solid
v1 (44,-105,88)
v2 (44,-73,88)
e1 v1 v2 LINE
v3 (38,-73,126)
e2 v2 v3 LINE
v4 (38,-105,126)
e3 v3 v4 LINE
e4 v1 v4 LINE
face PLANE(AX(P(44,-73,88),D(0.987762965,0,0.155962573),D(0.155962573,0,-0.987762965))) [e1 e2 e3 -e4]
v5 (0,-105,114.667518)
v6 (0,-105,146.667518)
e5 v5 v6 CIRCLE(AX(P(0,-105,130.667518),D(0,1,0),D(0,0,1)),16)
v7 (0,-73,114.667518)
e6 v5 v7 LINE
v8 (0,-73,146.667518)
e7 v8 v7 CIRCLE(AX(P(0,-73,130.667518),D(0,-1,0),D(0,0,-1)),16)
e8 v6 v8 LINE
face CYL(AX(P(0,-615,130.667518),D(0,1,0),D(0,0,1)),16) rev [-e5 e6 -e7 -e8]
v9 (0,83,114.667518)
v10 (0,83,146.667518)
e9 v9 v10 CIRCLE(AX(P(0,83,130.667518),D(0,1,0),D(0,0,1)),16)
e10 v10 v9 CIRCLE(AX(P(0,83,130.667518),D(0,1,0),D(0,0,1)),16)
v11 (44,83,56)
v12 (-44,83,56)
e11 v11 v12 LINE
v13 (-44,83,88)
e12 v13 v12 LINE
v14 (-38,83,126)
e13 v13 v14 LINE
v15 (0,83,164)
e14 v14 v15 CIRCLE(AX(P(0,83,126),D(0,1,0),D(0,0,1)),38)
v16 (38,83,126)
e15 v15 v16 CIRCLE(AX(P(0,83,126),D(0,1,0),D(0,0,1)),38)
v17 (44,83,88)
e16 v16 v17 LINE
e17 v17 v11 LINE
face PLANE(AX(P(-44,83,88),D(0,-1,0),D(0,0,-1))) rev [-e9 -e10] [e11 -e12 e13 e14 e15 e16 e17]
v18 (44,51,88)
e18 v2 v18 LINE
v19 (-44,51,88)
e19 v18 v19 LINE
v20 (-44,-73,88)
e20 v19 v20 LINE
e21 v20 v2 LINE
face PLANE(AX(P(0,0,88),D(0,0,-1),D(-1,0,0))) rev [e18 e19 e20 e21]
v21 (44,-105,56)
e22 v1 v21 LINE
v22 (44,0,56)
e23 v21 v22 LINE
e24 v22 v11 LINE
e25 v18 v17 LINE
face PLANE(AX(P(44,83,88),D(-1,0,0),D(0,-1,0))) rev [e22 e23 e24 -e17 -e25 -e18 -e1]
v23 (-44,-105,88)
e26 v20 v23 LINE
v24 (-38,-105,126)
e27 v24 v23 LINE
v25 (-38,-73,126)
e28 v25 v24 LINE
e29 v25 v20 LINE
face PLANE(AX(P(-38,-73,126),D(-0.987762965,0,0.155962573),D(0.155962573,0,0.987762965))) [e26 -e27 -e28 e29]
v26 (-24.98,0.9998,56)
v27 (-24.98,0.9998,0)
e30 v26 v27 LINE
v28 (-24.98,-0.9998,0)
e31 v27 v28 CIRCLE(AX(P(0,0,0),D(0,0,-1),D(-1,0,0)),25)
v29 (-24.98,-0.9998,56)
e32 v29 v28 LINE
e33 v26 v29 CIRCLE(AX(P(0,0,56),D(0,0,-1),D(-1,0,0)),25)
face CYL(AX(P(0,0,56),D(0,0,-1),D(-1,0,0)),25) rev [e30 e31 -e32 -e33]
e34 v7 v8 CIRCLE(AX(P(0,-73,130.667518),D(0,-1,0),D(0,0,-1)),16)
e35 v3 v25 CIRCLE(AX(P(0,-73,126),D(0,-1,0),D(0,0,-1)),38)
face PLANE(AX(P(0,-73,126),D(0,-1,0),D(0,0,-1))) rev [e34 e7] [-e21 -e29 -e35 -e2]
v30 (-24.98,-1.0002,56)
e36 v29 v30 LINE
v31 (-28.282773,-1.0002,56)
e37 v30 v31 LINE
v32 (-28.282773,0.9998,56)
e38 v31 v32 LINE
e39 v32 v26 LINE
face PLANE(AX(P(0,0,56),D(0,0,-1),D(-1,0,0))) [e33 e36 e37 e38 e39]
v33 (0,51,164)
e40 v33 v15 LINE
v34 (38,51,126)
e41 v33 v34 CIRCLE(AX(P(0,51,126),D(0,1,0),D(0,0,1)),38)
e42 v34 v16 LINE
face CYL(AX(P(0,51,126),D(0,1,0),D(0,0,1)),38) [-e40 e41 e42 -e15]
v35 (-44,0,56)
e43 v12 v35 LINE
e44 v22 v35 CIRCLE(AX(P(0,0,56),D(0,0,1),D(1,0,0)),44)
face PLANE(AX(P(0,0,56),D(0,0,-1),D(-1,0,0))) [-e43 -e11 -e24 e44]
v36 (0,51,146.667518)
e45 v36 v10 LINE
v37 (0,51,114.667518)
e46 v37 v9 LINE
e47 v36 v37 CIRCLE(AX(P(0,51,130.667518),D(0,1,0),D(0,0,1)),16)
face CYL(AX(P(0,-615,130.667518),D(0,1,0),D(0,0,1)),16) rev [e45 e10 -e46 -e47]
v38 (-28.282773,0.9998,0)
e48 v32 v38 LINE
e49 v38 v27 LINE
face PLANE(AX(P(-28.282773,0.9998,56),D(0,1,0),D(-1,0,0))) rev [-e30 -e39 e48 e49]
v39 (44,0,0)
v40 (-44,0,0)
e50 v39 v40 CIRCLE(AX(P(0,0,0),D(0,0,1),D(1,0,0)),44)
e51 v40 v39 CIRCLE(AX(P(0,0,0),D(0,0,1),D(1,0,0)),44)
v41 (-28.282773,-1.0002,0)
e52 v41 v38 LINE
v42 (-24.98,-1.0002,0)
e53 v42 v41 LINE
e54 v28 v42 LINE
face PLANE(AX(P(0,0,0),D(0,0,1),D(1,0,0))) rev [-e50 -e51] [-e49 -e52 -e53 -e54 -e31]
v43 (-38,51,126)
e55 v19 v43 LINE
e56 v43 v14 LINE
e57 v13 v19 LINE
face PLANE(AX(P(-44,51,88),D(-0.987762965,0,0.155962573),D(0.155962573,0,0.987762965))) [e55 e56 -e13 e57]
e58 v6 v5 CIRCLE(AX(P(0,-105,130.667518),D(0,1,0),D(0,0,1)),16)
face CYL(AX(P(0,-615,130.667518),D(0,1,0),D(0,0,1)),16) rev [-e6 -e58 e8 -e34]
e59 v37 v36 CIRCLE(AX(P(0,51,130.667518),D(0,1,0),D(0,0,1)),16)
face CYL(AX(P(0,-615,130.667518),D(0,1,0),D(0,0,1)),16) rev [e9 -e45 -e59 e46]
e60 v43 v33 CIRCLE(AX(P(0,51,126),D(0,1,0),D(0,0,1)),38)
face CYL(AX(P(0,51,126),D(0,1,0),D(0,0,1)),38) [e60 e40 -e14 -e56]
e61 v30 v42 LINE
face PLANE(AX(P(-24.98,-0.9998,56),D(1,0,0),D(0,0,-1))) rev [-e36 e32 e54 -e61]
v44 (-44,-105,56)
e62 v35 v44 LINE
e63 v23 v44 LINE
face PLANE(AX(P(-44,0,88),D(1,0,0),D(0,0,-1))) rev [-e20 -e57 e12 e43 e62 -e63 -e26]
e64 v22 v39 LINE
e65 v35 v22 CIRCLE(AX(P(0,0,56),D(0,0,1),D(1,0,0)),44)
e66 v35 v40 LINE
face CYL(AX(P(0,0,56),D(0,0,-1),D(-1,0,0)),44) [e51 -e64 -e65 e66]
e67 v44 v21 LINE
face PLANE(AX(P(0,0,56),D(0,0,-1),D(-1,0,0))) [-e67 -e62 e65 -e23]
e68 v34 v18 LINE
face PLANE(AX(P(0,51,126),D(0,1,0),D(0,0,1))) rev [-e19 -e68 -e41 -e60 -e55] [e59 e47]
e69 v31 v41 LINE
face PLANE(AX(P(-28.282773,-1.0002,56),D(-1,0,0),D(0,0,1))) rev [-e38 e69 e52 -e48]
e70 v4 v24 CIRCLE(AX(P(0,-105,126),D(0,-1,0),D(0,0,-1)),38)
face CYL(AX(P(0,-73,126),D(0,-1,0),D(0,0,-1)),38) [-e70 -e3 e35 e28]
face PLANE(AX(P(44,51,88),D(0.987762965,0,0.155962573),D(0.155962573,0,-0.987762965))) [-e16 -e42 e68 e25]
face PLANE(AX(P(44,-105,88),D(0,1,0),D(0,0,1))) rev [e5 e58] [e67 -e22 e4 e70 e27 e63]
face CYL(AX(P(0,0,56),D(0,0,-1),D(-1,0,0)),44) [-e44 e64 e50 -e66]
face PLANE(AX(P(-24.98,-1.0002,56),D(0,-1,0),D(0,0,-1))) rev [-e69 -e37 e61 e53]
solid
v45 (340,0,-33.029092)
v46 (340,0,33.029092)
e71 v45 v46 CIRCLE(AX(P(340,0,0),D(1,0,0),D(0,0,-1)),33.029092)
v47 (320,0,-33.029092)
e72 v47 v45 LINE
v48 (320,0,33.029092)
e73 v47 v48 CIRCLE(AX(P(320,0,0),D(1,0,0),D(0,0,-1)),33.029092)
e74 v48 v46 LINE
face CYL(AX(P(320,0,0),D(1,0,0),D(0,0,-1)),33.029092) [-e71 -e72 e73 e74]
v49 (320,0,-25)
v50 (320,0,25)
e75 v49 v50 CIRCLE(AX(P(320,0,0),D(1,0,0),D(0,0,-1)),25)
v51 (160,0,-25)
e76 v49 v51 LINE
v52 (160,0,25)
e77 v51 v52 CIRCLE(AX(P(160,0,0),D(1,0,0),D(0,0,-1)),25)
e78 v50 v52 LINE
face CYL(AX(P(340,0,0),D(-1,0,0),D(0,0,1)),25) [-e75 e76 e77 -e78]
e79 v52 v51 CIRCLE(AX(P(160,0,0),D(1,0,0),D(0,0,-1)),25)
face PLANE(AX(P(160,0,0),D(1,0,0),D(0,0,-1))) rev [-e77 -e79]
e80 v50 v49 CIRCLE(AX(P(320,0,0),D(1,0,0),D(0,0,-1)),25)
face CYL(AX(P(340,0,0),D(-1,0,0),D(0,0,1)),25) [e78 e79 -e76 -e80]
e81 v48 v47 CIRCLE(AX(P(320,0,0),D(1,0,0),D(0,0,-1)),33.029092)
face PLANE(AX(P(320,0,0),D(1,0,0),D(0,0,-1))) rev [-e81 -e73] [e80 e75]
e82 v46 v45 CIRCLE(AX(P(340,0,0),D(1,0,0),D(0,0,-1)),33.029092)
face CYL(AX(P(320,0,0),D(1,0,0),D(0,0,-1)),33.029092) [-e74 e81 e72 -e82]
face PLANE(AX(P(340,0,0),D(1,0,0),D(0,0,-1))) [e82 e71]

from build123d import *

# Parameters (mm, degrees)
HUB_PROFILE_88_R                  = 44
HUB_BOSS_88_DEPTH                 = 56
HUB_CUT_DEPTH                     = 56
YOKE_BASE_PLATE_DEPTH             = 32
YOKE_ARMS_DEPTH                   = 32
YOKE_START                        = -32
YOKE_WEB_DEPTH                    = 32
CROSS_PIN_BORE_PROFILE_R          = 16
CROSS_PIN_BORE_THROUGH_LUGS_DEPTH = 698
PIN_SHAFT_PROFILE_50_R            = 25
PIN_SHAFT_50_DEPTH                = 180
PIN_HEAD_PROFILE_R                = 33.029092334
PIN_HEAD_DEPTH                    = 20


with BuildPart() as part:
    # Hub Profile Ø88 → Hub Boss Ø88 (new body)
    with BuildSketch(Plane.XY):
        Circle(HUB_PROFILE_88_R)
    extrude(amount=HUB_BOSS_88_DEPTH)

    # Hub Cut Profile → Hub Cut (cut)
    with BuildSketch(Plane(origin=(0, 0, 0), x_dir=(-1, 0, 0), z_dir=(0, 0, -1))):
        with BuildLine():
            Line((24.98, -0.99979998), (28.282772946, -1.00020002))
            Line((28.282772946, -1.00020002), (28.282772946, 0.99979998))
            Line((28.282772946, 0.99979998), (24.98, 0.99979998))
            ThreePointArc((24.98, 0.99979998), (-25, 0), (24.98, -0.99979998))
        make_face()
    extrude(amount=-HUB_CUT_DEPTH, mode=Mode.SUBTRACT)

    # Yoke Base Profile → Yoke Base Plate (add)
    with BuildSketch(Plane.XY.offset(56)):
        Polygon((-44, 0), (-44, 83), (44, 83), (44, -105), (-44, -105), align=None)
    extrude(amount=YOKE_BASE_PLATE_DEPTH)

    # Yoke Arms Profile → Yoke Arms (add)
    with BuildSketch(Plane(origin=(0, 83, 0), x_dir=(1, 0, 0), z_dir=(0, 1, 0))):
        with BuildLine():
            Line((-44, -88), (44, -88))
            Line((44, -88), (38, -126))
            ThreePointArc((38, -126), (0, -164), (-38, -126))
            Line((-38, -126), (-44, -88))
        make_face()
    extrude(amount=-YOKE_ARMS_DEPTH)

    # Yoke Web Profile → Yoke Web (add)
    with BuildSketch(Plane.XZ.offset(105).offset(YOKE_START)):
        with BuildLine():
            Line((-38, 126), (-44, 88))
            Line((-44, 88), (44, 88))
            Line((44, 88), (38, 126))
            ThreePointArc((38, 126), (0, 164), (-38, 126))
        make_face()
    extrude(amount=YOKE_WEB_DEPTH)

    # Cross Pin Bore Profile → Cross Pin Bore Through Lugs (cut)
    with BuildSketch(Plane(origin=(0, 83, 0), x_dir=(1, 0, 0), z_dir=(0, 1, 0))):
        with Locations(Location((0, -130.667517764, 0), (0, 0, 270))):
            Circle(CROSS_PIN_BORE_PROFILE_R)
    extrude(amount=-CROSS_PIN_BORE_THROUGH_LUGS_DEPTH, mode=Mode.SUBTRACT)


with BuildPart() as body_2:
    # Pin Shaft Profile Ø50 → Pin Shaft Ø50 (new body)
    with BuildSketch(Plane(origin=(160, 0, 0), x_dir=(0, 0, -1), z_dir=(1, 0, 0))):
        with Locations(Location((0, 0, 0), (0, 0, 180))):
            Circle(PIN_SHAFT_PROFILE_50_R)
    extrude(amount=PIN_SHAFT_50_DEPTH)

    # Pin Head Profile → Pin Head (add)
    with BuildSketch(Plane(origin=(340, 0, 0), x_dir=(0, 0, -1), z_dir=(1, 0, 0))):
        Circle(PIN_HEAD_PROFILE_R)
    extrude(amount=-PIN_HEAD_DEPTH)


solid = Compound([part.part, body_2.part])
